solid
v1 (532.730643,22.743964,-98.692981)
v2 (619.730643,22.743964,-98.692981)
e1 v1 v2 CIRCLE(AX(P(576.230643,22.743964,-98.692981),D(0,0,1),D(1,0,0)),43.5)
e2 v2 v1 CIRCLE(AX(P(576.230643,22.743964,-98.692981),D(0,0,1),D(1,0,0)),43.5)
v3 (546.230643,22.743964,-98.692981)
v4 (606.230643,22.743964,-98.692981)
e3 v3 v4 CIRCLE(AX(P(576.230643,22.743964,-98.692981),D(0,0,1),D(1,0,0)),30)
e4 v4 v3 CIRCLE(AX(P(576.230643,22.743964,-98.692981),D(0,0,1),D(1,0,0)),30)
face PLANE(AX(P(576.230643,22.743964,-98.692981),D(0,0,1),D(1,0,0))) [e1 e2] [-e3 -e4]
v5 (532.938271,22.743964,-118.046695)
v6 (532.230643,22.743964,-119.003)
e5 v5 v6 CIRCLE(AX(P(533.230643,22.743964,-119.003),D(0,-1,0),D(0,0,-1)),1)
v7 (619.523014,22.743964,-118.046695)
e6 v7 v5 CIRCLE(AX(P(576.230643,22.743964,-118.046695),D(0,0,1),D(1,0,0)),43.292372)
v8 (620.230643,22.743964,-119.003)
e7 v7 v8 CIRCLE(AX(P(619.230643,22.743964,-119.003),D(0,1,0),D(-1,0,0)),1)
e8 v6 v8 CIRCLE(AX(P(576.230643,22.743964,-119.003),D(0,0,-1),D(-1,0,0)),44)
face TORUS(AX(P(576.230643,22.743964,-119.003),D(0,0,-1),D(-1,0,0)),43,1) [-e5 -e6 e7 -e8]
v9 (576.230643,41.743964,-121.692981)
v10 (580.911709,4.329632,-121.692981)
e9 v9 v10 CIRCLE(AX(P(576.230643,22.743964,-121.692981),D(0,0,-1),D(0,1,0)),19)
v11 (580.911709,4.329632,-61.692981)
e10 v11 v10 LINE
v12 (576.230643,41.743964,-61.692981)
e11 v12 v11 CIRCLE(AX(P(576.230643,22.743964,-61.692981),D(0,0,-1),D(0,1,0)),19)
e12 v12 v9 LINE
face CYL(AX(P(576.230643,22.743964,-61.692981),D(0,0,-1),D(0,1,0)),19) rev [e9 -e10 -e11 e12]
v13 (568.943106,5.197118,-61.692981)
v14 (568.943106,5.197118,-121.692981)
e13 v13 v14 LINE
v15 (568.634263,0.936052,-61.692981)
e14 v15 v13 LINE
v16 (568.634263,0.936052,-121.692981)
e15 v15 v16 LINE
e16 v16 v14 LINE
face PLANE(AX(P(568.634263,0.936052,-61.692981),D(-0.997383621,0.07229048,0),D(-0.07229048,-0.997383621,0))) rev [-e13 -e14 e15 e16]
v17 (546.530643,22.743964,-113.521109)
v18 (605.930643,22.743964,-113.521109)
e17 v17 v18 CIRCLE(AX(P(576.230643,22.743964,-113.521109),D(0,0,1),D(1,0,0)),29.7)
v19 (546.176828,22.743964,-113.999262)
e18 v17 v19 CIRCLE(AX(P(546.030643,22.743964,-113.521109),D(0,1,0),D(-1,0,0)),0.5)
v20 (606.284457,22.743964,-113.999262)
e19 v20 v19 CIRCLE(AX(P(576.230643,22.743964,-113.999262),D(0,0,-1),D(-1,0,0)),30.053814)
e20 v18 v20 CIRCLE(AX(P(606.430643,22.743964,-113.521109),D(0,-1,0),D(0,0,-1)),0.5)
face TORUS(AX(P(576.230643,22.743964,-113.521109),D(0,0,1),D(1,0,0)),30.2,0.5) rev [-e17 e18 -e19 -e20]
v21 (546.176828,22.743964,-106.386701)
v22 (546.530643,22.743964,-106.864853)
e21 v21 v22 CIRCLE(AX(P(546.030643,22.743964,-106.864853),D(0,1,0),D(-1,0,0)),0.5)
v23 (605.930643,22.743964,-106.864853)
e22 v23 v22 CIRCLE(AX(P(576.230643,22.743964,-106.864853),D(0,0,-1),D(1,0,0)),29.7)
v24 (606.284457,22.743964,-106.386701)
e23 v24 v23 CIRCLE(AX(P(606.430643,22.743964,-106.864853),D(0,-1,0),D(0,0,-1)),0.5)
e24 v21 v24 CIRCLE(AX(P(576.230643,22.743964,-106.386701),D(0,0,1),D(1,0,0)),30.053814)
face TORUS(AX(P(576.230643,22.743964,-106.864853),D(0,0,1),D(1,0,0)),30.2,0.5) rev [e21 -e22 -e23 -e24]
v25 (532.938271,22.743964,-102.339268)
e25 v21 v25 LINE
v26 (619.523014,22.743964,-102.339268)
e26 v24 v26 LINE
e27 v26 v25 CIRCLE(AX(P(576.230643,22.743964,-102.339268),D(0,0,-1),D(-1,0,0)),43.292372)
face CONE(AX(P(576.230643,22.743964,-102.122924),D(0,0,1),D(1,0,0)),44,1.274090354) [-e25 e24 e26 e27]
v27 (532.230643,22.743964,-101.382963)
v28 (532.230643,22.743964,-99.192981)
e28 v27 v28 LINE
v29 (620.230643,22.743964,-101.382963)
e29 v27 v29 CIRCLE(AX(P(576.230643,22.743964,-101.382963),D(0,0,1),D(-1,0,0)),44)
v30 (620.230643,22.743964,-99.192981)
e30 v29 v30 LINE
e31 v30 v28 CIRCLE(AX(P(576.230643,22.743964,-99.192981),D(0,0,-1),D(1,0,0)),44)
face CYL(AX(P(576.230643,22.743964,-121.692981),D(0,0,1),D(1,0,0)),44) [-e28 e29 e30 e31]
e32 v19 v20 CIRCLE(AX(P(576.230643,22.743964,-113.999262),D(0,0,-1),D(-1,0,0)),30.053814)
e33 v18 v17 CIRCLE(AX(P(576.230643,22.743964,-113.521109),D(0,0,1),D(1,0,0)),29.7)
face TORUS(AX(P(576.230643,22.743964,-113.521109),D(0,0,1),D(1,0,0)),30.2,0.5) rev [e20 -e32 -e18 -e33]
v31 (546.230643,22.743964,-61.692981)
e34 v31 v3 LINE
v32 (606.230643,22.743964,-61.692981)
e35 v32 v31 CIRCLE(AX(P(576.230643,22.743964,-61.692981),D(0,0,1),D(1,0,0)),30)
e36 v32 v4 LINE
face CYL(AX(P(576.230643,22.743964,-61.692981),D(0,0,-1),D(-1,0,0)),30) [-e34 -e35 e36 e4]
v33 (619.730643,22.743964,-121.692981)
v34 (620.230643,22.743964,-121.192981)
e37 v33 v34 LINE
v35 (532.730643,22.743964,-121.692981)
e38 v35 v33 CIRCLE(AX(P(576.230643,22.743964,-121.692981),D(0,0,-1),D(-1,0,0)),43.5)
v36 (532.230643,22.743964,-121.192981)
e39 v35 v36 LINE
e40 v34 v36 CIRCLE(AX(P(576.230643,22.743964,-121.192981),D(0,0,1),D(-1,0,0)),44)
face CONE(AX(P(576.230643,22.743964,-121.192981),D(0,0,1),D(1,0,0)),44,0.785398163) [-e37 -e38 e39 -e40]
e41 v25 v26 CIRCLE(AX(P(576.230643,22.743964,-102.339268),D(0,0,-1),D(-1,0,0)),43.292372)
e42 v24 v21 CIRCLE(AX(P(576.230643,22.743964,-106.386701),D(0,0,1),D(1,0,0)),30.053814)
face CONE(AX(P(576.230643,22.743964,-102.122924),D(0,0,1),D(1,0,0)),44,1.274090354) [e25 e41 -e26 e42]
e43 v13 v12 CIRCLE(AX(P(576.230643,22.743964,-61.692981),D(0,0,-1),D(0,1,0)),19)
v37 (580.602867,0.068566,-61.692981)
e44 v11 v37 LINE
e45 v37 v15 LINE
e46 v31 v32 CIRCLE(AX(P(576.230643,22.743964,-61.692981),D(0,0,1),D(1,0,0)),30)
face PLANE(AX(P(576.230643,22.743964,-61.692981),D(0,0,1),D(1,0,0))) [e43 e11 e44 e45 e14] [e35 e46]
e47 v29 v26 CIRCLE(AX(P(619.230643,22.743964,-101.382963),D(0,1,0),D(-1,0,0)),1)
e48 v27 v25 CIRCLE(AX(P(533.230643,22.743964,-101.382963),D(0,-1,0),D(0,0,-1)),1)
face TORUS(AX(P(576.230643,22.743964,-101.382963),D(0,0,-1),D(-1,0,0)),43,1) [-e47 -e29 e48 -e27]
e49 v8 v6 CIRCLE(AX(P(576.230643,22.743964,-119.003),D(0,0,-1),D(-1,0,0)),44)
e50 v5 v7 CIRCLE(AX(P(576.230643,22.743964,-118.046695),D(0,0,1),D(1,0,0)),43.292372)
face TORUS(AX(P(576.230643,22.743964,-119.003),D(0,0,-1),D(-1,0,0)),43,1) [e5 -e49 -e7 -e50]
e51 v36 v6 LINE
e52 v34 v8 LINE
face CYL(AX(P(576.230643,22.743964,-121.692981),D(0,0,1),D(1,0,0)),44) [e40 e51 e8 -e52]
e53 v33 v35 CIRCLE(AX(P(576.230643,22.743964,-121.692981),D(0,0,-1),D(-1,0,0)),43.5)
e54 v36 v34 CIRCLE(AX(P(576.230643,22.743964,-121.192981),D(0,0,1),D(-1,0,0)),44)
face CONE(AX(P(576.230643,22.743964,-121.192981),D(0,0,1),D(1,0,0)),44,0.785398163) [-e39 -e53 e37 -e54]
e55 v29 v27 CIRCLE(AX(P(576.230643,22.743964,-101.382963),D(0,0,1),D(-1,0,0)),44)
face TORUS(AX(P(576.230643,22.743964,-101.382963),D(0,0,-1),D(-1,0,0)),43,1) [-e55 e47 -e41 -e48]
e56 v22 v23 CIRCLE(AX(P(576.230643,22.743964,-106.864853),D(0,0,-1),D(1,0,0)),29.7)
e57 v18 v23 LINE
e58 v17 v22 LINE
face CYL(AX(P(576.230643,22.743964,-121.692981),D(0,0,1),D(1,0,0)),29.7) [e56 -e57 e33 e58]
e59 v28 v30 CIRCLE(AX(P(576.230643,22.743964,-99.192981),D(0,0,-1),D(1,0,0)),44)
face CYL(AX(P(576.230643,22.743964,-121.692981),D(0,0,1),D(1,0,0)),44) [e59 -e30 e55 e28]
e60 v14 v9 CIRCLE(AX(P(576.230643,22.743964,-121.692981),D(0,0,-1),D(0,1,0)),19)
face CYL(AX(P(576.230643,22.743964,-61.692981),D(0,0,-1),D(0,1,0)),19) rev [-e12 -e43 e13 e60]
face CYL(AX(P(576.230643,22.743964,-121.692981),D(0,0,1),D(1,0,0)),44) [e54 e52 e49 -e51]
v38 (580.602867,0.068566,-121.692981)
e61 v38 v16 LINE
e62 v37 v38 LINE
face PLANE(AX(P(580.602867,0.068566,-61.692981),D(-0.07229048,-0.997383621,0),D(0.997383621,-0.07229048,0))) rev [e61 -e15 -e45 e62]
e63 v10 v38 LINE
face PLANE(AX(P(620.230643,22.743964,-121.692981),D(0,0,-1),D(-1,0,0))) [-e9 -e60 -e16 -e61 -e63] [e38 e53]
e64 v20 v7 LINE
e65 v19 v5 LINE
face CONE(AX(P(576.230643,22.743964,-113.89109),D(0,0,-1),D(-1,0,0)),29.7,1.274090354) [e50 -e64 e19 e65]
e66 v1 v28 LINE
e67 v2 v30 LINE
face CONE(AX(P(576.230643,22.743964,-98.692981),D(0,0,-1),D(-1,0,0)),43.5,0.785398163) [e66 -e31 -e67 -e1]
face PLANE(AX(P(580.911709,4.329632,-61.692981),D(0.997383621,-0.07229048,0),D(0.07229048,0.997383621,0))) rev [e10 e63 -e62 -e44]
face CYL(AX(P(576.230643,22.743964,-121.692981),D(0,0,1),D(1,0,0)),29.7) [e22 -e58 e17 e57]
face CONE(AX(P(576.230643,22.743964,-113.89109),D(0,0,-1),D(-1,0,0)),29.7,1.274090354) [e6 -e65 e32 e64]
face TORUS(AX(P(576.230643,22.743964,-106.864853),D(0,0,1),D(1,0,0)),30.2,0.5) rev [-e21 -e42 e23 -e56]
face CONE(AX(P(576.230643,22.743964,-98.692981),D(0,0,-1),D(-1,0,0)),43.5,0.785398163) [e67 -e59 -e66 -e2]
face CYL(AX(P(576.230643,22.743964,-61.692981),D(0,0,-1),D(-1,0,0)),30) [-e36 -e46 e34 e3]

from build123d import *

# Parameters (mm, degrees)
SKETCH2_R           = 30
BOSS_EXTRUDE1_DEPTH = 37
CUT_EXTRUDE1_DEPTH  = 627.690359496
SKETCH4_W           = 19
SKETCH4_H           = 60
CHAMFER1_SIZE       = 0.5
FILLET1_R           = 0.5
FILLET2_R           = 1


with BuildPart() as part:
    # Sketch1 → Revolve1 (revolve)
    with BuildSketch(Plane(origin=(0, 22.743963655, 0), x_dir=(1, 0, 0), z_dir=(0, 1, 0))):
        Polygon((620.230642584, 121.692981355), (576.230642584, 121.692981355), (576.230642584, 98.692981355), (620.230642584, 98.692981355), (620.230642584, 102.12292397), (605.930642584, 106.494872715), (605.930642584, 113.891089995), (620.230642584, 118.26303874), align=None)
    revolve(axis=Axis((576.230642584, 22.743963655, -121.692981355), (0, 0, 1)))

    # Sketch2 → Boss-Extrude1 (add)
    with BuildSketch(Plane.XY.offset(-98.692981355)):
        with Locations((576.230642584, 22.743963655)):
            Circle(SKETCH2_R)
    extrude(amount=BOSS_EXTRUDE1_DEPTH)

    # Sketch3 → Cut-Extrude1 (cut, through all)
    with BuildSketch(Plane(origin=(0, 0, -121.692981355), x_dir=(-1, 0, 0), z_dir=(0, 0, -1))):
        with BuildLine():
            Line((-580.602866602, 0.068566036), (-568.634263156, 0.936051797))
            Line((-568.634263156, 0.936051797), (-568.943105698, 5.197117609))
            ThreePointArc((-568.943105698, 5.197117609), (-574.857123463, 3.793674865), (-580.911709145, 4.329631849))
            Line((-580.911709145, 4.329631849), (-580.602866602, 0.068566036))
        make_face()
    extrude(amount=-CUT_EXTRUDE1_DEPTH, mode=Mode.SUBTRACT)

    # Sketch4 → Cut-Revolve1 (revolve, cut)
    with BuildSketch(Plane.XZ.offset(-22.743963655)):
        with Locations((585.730642584, -91.692981355)):
            Rectangle(SKETCH4_W, SKETCH4_H)
    revolve(axis=Axis((576.230642584, 22.743963655, -61.692981355), (0, 0, -1)), mode=Mode.SUBTRACT)

    # Chamfer1
    chamfer1_edges = [part.edges().sort_by_distance(p)[0] for p in [
        (532.230642584, 22.743963655, -98.692981355),
        (532.230642584, 22.743963655, -121.692981355),
    ]]
    chamfer(chamfer1_edges, length=CHAMFER1_SIZE)

    # Fillet1
    fillet1_edges = [part.edges().sort_by_distance(p)[0] for p in [
        (546.530642584, 22.743963655, -113.891089995),
        (546.530642584, 22.743963655, -106.494872715),
    ]]
    fillet(fillet1_edges, radius=FILLET1_R)

    # Fillet2
    fillet2_edges = [part.edges().sort_by_distance(p)[0] for p in [
        (532.230642584, 22.743963655, -118.26303874),
        (532.230642584, 22.743963655, -102.12292397),
    ]]
    fillet(fillet2_edges, radius=FILLET2_R)


solid = part.part
